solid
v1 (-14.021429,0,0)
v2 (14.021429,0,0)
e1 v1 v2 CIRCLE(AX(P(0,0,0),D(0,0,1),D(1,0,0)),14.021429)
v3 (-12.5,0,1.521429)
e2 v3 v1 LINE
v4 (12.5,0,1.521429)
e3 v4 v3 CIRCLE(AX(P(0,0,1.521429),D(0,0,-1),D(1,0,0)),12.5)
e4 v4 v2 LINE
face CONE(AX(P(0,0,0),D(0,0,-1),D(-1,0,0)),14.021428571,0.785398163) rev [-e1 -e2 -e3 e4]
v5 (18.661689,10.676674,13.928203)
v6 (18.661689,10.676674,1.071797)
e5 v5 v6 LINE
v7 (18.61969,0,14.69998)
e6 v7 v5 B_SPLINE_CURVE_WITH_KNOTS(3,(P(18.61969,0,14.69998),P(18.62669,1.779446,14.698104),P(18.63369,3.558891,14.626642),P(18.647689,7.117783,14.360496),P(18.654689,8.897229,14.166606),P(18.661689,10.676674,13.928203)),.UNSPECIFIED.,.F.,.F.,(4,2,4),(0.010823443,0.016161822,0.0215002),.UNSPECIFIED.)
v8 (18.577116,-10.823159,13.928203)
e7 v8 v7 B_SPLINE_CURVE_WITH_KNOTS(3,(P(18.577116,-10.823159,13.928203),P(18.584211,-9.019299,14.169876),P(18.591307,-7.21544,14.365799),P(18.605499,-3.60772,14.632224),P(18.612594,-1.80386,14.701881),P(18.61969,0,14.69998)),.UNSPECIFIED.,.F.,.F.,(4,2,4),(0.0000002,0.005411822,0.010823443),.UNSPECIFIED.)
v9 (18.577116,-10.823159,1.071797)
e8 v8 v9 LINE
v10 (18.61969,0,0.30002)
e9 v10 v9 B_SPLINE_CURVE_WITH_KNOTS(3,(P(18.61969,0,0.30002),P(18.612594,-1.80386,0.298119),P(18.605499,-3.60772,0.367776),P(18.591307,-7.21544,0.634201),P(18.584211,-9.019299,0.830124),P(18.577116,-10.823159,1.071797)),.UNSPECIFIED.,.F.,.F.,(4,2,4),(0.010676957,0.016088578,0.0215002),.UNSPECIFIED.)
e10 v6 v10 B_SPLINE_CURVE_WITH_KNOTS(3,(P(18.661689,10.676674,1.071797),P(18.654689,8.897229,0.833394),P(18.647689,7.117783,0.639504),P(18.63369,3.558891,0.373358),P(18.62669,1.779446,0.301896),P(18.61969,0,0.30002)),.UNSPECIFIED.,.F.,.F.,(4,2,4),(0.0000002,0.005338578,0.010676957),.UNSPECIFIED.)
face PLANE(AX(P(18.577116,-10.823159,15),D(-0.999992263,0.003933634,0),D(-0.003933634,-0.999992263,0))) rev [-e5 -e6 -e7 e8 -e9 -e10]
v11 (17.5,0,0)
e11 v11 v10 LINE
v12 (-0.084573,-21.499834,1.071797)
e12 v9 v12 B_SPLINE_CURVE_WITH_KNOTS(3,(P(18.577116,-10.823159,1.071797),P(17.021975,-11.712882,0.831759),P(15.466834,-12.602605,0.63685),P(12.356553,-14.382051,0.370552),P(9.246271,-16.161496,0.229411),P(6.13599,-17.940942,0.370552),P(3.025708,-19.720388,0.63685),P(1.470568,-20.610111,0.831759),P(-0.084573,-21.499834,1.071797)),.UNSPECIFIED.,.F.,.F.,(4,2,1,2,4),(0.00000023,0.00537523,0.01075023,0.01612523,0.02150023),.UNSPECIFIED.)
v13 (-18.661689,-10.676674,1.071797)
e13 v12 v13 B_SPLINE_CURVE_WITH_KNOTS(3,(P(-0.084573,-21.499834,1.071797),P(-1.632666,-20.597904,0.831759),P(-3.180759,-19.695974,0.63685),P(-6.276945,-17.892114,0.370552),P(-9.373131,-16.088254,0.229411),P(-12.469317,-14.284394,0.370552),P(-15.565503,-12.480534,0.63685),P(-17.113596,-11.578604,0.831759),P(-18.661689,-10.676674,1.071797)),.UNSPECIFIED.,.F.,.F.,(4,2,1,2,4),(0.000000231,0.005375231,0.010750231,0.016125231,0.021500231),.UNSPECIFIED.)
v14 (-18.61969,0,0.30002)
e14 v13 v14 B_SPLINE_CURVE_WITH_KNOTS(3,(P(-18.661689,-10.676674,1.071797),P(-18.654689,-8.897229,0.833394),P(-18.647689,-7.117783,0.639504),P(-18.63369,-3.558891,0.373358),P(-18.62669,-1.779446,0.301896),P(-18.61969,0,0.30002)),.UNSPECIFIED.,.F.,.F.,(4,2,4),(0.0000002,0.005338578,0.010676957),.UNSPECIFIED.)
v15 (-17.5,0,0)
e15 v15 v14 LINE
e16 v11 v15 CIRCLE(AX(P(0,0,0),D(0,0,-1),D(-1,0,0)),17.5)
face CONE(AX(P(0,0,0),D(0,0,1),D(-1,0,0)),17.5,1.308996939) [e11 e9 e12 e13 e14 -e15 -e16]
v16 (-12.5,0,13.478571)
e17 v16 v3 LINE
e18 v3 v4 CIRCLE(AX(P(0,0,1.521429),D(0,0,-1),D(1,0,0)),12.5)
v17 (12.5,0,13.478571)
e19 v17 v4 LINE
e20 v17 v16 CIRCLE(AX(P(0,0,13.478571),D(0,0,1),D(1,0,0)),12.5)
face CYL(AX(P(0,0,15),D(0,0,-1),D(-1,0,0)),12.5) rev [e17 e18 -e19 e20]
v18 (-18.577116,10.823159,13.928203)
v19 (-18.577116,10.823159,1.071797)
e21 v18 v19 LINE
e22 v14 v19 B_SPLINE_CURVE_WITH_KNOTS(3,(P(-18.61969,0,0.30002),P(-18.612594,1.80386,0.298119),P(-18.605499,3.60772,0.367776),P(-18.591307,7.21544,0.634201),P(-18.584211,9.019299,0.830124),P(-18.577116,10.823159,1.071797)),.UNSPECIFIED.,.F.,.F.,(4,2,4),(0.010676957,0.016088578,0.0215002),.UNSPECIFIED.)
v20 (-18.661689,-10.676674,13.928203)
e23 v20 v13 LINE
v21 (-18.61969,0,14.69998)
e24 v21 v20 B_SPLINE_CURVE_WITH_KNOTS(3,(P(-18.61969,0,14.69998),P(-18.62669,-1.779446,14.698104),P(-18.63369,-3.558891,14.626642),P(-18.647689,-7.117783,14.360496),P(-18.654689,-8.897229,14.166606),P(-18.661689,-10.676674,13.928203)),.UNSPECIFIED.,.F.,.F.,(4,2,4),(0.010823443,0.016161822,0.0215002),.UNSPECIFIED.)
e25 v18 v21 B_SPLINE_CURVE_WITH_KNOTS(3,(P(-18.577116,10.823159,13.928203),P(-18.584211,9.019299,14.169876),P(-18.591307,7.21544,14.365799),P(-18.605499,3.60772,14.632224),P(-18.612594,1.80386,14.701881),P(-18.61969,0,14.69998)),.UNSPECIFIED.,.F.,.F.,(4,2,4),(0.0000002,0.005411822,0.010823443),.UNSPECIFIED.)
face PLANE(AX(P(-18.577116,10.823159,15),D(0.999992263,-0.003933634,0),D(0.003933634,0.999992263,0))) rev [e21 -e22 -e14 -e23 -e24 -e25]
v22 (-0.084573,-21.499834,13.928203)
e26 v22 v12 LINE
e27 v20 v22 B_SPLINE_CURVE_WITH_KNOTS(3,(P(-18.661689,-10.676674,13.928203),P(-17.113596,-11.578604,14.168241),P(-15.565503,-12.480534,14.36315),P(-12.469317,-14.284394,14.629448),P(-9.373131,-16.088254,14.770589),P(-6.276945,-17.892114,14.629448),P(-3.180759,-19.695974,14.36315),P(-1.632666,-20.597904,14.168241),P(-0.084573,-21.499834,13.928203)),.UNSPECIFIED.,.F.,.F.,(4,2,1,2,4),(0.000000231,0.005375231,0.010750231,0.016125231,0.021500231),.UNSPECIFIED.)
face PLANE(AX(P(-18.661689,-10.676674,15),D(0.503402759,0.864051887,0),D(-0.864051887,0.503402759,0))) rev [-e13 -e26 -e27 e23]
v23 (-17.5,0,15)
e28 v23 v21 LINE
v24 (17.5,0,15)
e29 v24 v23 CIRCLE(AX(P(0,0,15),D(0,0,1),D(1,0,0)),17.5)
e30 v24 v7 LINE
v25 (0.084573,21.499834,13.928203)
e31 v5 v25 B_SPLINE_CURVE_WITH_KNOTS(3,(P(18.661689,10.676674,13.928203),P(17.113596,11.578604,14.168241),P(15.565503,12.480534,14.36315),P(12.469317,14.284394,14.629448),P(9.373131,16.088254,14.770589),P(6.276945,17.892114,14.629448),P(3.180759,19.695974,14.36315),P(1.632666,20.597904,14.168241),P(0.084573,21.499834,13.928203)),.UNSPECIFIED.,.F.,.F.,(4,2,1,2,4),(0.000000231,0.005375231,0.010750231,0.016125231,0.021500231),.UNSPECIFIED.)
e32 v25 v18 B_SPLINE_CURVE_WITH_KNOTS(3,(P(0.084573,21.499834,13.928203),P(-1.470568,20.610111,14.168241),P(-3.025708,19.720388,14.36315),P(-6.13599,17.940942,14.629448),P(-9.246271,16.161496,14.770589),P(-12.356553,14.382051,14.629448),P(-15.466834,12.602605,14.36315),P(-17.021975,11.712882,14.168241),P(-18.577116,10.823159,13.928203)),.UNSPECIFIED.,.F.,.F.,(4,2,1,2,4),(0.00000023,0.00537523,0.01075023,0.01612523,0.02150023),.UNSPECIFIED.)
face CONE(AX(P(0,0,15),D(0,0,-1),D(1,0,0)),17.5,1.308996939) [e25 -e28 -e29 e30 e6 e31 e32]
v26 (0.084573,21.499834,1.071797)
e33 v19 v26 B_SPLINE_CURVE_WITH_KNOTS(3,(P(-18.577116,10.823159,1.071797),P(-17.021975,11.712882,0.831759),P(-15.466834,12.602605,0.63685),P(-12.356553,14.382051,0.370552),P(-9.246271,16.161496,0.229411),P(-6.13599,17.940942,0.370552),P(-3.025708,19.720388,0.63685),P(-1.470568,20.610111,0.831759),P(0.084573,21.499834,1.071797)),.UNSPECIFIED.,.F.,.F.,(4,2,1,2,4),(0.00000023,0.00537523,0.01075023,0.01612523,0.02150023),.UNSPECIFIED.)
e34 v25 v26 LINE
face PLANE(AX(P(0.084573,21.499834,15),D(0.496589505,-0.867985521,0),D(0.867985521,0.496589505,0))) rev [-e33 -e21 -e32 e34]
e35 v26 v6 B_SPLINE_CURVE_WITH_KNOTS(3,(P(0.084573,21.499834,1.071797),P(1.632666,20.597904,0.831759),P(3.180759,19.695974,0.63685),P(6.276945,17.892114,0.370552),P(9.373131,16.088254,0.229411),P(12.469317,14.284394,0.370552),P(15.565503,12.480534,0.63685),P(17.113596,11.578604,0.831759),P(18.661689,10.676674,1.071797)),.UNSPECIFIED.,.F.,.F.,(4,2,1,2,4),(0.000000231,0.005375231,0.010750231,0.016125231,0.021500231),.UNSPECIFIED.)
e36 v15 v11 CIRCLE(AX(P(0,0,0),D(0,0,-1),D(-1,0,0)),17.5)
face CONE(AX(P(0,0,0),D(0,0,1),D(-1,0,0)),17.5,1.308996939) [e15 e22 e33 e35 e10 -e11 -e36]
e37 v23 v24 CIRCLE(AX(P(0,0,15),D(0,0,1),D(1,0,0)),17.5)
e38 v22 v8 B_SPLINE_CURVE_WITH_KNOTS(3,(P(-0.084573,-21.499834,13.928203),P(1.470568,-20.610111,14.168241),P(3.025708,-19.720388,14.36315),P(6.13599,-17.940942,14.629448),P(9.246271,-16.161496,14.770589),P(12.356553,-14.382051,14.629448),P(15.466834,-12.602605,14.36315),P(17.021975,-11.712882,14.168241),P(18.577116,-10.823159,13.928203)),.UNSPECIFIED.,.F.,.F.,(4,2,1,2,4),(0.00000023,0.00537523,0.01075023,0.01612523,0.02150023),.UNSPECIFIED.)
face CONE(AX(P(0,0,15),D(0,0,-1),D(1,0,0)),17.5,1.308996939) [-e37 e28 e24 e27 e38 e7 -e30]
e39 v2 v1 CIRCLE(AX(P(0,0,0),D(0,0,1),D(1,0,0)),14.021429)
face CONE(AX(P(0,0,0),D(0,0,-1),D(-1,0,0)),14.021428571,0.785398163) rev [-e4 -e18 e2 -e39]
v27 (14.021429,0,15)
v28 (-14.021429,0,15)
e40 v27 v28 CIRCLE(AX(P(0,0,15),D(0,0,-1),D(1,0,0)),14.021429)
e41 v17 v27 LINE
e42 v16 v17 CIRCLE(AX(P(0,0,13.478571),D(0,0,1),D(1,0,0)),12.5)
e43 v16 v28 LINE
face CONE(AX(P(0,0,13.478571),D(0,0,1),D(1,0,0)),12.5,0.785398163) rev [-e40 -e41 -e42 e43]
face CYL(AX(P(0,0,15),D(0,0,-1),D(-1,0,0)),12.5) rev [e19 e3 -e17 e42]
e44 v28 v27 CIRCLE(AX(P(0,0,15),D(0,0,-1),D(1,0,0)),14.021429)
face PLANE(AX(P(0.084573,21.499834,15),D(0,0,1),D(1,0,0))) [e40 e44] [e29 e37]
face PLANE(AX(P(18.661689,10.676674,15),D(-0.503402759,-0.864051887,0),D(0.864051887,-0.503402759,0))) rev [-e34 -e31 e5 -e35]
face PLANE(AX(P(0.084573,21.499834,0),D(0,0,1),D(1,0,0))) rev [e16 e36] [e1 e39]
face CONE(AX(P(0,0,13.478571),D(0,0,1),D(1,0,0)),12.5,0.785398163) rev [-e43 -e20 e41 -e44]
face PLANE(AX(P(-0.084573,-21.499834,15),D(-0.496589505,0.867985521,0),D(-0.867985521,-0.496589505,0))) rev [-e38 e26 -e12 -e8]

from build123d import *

# Parameters (mm, degrees)
SKETCH1_R          = 12.5
BASE_EXTRUDE_DEPTH = 15
SKETCH2_OUTSIDE_W  = 298.754
SKETCH2_OUTSIDE_H  = 304.43
SKETCH2_OUTSIDE_R  = 17.5
CUT_EXTRUDE1_DEPTH = 33.179208695
CUT_EXTRUDE1_DRAFT = -75
SKETCH3_OUTSIDE_W  = 298.754
SKETCH3_OUTSIDE_H  = 304.43
SKETCH3_OUTSIDE_R  = 17.5
CUT_EXTRUDE2_DEPTH = 33.179208695
CUT_EXTRUDE2_DRAFT = -75
CHAMFER1_SIZE      = 1.521428571


with BuildPart() as part:
    # Sketch1 → Base-Extrude (new body)
    with BuildSketch(Plane.XY):
        Polygon((0.084573131, 21.499833659), (-18.577115561, 10.823159309), (-18.661688692, -10.67667435), (-0.084573131, -21.499833659), (18.577115561, -10.823159309), (18.661688692, 10.67667435), align=None)
        Circle(SKETCH1_R, mode=Mode.SUBTRACT)
    extrude(amount=BASE_EXTRUDE_DEPTH)


with BuildPart() as cut_extrude1_tool:
    # Sketch2 outside → Cut-Extrude1 (with draft: the straight prism first)
    with BuildSketch(Plane(origin=(0, 0, 0), x_dir=(-1, 0, 0), z_dir=(0, 0, -1))):
        Rectangle(SKETCH2_OUTSIDE_W, SKETCH2_OUTSIDE_H)
        Circle(SKETCH2_OUTSIDE_R, mode=Mode.SUBTRACT)
    extrude(amount=-CUT_EXTRUDE1_DEPTH)
    # Cut-Extrude1: the draft: its side faces are tilted about the plane it starts from
    cut_extrude1_sides = [cut_extrude1_tool.faces().sort_by_distance(p)[0] for p in [
        (0, -152.215, 16.589604347),
        (-149.377, 0, 16.589604347),
        (0, 152.215, 16.589604347),
        (149.377, 0, 16.589604347),
        (17.5, 0, 16.589604347),
    ]]
    draft(cut_extrude1_sides, Plane(origin=(0, 0, 0), x_dir=(-1, 0, 0), z_dir=(0, 0, -1)), CUT_EXTRUDE1_DRAFT)


with BuildPart() as part_1:
    add(part.part)

    # Cut-Extrude1: cut by cut_extrude1_tool
    add(cut_extrude1_tool.part, mode=Mode.SUBTRACT)


with BuildPart() as cut_extrude2_tool:
    # Sketch3 outside → Cut-Extrude2 (with draft: the straight prism first)
    with BuildSketch(Plane.XY.offset(15)):
        Rectangle(SKETCH3_OUTSIDE_W, SKETCH3_OUTSIDE_H)
        Circle(SKETCH3_OUTSIDE_R, mode=Mode.SUBTRACT)
    extrude(amount=-CUT_EXTRUDE2_DEPTH)
    # Cut-Extrude2: the draft: its side faces are tilted about the plane it starts from
    cut_extrude2_sides = [cut_extrude2_tool.faces().sort_by_distance(p)[0] for p in [
        (0, -152.215, -1.589604347),
        (149.377, 0, -1.589604347),
        (0, 152.215, -1.589604347),
        (-149.377, 0, -1.589604347),
        (-17.5, 0, -1.589604347),
    ]]
    draft(cut_extrude2_sides, Plane.XY.offset(15), CUT_EXTRUDE2_DRAFT)


with BuildPart() as part_2:
    add(part_1.part)

    # Cut-Extrude2: cut by cut_extrude2_tool
    add(cut_extrude2_tool.part, mode=Mode.SUBTRACT)

    # Chamfer1
    chamfer1_edges = [part_2.edges().sort_by_distance(p)[0] for p in [
        (-12.5, 0, 0),
        (-12.5, 0, 15),
    ]]
    chamfer(chamfer1_edges, length=CHAMFER1_SIZE)


solid = part_2.part
